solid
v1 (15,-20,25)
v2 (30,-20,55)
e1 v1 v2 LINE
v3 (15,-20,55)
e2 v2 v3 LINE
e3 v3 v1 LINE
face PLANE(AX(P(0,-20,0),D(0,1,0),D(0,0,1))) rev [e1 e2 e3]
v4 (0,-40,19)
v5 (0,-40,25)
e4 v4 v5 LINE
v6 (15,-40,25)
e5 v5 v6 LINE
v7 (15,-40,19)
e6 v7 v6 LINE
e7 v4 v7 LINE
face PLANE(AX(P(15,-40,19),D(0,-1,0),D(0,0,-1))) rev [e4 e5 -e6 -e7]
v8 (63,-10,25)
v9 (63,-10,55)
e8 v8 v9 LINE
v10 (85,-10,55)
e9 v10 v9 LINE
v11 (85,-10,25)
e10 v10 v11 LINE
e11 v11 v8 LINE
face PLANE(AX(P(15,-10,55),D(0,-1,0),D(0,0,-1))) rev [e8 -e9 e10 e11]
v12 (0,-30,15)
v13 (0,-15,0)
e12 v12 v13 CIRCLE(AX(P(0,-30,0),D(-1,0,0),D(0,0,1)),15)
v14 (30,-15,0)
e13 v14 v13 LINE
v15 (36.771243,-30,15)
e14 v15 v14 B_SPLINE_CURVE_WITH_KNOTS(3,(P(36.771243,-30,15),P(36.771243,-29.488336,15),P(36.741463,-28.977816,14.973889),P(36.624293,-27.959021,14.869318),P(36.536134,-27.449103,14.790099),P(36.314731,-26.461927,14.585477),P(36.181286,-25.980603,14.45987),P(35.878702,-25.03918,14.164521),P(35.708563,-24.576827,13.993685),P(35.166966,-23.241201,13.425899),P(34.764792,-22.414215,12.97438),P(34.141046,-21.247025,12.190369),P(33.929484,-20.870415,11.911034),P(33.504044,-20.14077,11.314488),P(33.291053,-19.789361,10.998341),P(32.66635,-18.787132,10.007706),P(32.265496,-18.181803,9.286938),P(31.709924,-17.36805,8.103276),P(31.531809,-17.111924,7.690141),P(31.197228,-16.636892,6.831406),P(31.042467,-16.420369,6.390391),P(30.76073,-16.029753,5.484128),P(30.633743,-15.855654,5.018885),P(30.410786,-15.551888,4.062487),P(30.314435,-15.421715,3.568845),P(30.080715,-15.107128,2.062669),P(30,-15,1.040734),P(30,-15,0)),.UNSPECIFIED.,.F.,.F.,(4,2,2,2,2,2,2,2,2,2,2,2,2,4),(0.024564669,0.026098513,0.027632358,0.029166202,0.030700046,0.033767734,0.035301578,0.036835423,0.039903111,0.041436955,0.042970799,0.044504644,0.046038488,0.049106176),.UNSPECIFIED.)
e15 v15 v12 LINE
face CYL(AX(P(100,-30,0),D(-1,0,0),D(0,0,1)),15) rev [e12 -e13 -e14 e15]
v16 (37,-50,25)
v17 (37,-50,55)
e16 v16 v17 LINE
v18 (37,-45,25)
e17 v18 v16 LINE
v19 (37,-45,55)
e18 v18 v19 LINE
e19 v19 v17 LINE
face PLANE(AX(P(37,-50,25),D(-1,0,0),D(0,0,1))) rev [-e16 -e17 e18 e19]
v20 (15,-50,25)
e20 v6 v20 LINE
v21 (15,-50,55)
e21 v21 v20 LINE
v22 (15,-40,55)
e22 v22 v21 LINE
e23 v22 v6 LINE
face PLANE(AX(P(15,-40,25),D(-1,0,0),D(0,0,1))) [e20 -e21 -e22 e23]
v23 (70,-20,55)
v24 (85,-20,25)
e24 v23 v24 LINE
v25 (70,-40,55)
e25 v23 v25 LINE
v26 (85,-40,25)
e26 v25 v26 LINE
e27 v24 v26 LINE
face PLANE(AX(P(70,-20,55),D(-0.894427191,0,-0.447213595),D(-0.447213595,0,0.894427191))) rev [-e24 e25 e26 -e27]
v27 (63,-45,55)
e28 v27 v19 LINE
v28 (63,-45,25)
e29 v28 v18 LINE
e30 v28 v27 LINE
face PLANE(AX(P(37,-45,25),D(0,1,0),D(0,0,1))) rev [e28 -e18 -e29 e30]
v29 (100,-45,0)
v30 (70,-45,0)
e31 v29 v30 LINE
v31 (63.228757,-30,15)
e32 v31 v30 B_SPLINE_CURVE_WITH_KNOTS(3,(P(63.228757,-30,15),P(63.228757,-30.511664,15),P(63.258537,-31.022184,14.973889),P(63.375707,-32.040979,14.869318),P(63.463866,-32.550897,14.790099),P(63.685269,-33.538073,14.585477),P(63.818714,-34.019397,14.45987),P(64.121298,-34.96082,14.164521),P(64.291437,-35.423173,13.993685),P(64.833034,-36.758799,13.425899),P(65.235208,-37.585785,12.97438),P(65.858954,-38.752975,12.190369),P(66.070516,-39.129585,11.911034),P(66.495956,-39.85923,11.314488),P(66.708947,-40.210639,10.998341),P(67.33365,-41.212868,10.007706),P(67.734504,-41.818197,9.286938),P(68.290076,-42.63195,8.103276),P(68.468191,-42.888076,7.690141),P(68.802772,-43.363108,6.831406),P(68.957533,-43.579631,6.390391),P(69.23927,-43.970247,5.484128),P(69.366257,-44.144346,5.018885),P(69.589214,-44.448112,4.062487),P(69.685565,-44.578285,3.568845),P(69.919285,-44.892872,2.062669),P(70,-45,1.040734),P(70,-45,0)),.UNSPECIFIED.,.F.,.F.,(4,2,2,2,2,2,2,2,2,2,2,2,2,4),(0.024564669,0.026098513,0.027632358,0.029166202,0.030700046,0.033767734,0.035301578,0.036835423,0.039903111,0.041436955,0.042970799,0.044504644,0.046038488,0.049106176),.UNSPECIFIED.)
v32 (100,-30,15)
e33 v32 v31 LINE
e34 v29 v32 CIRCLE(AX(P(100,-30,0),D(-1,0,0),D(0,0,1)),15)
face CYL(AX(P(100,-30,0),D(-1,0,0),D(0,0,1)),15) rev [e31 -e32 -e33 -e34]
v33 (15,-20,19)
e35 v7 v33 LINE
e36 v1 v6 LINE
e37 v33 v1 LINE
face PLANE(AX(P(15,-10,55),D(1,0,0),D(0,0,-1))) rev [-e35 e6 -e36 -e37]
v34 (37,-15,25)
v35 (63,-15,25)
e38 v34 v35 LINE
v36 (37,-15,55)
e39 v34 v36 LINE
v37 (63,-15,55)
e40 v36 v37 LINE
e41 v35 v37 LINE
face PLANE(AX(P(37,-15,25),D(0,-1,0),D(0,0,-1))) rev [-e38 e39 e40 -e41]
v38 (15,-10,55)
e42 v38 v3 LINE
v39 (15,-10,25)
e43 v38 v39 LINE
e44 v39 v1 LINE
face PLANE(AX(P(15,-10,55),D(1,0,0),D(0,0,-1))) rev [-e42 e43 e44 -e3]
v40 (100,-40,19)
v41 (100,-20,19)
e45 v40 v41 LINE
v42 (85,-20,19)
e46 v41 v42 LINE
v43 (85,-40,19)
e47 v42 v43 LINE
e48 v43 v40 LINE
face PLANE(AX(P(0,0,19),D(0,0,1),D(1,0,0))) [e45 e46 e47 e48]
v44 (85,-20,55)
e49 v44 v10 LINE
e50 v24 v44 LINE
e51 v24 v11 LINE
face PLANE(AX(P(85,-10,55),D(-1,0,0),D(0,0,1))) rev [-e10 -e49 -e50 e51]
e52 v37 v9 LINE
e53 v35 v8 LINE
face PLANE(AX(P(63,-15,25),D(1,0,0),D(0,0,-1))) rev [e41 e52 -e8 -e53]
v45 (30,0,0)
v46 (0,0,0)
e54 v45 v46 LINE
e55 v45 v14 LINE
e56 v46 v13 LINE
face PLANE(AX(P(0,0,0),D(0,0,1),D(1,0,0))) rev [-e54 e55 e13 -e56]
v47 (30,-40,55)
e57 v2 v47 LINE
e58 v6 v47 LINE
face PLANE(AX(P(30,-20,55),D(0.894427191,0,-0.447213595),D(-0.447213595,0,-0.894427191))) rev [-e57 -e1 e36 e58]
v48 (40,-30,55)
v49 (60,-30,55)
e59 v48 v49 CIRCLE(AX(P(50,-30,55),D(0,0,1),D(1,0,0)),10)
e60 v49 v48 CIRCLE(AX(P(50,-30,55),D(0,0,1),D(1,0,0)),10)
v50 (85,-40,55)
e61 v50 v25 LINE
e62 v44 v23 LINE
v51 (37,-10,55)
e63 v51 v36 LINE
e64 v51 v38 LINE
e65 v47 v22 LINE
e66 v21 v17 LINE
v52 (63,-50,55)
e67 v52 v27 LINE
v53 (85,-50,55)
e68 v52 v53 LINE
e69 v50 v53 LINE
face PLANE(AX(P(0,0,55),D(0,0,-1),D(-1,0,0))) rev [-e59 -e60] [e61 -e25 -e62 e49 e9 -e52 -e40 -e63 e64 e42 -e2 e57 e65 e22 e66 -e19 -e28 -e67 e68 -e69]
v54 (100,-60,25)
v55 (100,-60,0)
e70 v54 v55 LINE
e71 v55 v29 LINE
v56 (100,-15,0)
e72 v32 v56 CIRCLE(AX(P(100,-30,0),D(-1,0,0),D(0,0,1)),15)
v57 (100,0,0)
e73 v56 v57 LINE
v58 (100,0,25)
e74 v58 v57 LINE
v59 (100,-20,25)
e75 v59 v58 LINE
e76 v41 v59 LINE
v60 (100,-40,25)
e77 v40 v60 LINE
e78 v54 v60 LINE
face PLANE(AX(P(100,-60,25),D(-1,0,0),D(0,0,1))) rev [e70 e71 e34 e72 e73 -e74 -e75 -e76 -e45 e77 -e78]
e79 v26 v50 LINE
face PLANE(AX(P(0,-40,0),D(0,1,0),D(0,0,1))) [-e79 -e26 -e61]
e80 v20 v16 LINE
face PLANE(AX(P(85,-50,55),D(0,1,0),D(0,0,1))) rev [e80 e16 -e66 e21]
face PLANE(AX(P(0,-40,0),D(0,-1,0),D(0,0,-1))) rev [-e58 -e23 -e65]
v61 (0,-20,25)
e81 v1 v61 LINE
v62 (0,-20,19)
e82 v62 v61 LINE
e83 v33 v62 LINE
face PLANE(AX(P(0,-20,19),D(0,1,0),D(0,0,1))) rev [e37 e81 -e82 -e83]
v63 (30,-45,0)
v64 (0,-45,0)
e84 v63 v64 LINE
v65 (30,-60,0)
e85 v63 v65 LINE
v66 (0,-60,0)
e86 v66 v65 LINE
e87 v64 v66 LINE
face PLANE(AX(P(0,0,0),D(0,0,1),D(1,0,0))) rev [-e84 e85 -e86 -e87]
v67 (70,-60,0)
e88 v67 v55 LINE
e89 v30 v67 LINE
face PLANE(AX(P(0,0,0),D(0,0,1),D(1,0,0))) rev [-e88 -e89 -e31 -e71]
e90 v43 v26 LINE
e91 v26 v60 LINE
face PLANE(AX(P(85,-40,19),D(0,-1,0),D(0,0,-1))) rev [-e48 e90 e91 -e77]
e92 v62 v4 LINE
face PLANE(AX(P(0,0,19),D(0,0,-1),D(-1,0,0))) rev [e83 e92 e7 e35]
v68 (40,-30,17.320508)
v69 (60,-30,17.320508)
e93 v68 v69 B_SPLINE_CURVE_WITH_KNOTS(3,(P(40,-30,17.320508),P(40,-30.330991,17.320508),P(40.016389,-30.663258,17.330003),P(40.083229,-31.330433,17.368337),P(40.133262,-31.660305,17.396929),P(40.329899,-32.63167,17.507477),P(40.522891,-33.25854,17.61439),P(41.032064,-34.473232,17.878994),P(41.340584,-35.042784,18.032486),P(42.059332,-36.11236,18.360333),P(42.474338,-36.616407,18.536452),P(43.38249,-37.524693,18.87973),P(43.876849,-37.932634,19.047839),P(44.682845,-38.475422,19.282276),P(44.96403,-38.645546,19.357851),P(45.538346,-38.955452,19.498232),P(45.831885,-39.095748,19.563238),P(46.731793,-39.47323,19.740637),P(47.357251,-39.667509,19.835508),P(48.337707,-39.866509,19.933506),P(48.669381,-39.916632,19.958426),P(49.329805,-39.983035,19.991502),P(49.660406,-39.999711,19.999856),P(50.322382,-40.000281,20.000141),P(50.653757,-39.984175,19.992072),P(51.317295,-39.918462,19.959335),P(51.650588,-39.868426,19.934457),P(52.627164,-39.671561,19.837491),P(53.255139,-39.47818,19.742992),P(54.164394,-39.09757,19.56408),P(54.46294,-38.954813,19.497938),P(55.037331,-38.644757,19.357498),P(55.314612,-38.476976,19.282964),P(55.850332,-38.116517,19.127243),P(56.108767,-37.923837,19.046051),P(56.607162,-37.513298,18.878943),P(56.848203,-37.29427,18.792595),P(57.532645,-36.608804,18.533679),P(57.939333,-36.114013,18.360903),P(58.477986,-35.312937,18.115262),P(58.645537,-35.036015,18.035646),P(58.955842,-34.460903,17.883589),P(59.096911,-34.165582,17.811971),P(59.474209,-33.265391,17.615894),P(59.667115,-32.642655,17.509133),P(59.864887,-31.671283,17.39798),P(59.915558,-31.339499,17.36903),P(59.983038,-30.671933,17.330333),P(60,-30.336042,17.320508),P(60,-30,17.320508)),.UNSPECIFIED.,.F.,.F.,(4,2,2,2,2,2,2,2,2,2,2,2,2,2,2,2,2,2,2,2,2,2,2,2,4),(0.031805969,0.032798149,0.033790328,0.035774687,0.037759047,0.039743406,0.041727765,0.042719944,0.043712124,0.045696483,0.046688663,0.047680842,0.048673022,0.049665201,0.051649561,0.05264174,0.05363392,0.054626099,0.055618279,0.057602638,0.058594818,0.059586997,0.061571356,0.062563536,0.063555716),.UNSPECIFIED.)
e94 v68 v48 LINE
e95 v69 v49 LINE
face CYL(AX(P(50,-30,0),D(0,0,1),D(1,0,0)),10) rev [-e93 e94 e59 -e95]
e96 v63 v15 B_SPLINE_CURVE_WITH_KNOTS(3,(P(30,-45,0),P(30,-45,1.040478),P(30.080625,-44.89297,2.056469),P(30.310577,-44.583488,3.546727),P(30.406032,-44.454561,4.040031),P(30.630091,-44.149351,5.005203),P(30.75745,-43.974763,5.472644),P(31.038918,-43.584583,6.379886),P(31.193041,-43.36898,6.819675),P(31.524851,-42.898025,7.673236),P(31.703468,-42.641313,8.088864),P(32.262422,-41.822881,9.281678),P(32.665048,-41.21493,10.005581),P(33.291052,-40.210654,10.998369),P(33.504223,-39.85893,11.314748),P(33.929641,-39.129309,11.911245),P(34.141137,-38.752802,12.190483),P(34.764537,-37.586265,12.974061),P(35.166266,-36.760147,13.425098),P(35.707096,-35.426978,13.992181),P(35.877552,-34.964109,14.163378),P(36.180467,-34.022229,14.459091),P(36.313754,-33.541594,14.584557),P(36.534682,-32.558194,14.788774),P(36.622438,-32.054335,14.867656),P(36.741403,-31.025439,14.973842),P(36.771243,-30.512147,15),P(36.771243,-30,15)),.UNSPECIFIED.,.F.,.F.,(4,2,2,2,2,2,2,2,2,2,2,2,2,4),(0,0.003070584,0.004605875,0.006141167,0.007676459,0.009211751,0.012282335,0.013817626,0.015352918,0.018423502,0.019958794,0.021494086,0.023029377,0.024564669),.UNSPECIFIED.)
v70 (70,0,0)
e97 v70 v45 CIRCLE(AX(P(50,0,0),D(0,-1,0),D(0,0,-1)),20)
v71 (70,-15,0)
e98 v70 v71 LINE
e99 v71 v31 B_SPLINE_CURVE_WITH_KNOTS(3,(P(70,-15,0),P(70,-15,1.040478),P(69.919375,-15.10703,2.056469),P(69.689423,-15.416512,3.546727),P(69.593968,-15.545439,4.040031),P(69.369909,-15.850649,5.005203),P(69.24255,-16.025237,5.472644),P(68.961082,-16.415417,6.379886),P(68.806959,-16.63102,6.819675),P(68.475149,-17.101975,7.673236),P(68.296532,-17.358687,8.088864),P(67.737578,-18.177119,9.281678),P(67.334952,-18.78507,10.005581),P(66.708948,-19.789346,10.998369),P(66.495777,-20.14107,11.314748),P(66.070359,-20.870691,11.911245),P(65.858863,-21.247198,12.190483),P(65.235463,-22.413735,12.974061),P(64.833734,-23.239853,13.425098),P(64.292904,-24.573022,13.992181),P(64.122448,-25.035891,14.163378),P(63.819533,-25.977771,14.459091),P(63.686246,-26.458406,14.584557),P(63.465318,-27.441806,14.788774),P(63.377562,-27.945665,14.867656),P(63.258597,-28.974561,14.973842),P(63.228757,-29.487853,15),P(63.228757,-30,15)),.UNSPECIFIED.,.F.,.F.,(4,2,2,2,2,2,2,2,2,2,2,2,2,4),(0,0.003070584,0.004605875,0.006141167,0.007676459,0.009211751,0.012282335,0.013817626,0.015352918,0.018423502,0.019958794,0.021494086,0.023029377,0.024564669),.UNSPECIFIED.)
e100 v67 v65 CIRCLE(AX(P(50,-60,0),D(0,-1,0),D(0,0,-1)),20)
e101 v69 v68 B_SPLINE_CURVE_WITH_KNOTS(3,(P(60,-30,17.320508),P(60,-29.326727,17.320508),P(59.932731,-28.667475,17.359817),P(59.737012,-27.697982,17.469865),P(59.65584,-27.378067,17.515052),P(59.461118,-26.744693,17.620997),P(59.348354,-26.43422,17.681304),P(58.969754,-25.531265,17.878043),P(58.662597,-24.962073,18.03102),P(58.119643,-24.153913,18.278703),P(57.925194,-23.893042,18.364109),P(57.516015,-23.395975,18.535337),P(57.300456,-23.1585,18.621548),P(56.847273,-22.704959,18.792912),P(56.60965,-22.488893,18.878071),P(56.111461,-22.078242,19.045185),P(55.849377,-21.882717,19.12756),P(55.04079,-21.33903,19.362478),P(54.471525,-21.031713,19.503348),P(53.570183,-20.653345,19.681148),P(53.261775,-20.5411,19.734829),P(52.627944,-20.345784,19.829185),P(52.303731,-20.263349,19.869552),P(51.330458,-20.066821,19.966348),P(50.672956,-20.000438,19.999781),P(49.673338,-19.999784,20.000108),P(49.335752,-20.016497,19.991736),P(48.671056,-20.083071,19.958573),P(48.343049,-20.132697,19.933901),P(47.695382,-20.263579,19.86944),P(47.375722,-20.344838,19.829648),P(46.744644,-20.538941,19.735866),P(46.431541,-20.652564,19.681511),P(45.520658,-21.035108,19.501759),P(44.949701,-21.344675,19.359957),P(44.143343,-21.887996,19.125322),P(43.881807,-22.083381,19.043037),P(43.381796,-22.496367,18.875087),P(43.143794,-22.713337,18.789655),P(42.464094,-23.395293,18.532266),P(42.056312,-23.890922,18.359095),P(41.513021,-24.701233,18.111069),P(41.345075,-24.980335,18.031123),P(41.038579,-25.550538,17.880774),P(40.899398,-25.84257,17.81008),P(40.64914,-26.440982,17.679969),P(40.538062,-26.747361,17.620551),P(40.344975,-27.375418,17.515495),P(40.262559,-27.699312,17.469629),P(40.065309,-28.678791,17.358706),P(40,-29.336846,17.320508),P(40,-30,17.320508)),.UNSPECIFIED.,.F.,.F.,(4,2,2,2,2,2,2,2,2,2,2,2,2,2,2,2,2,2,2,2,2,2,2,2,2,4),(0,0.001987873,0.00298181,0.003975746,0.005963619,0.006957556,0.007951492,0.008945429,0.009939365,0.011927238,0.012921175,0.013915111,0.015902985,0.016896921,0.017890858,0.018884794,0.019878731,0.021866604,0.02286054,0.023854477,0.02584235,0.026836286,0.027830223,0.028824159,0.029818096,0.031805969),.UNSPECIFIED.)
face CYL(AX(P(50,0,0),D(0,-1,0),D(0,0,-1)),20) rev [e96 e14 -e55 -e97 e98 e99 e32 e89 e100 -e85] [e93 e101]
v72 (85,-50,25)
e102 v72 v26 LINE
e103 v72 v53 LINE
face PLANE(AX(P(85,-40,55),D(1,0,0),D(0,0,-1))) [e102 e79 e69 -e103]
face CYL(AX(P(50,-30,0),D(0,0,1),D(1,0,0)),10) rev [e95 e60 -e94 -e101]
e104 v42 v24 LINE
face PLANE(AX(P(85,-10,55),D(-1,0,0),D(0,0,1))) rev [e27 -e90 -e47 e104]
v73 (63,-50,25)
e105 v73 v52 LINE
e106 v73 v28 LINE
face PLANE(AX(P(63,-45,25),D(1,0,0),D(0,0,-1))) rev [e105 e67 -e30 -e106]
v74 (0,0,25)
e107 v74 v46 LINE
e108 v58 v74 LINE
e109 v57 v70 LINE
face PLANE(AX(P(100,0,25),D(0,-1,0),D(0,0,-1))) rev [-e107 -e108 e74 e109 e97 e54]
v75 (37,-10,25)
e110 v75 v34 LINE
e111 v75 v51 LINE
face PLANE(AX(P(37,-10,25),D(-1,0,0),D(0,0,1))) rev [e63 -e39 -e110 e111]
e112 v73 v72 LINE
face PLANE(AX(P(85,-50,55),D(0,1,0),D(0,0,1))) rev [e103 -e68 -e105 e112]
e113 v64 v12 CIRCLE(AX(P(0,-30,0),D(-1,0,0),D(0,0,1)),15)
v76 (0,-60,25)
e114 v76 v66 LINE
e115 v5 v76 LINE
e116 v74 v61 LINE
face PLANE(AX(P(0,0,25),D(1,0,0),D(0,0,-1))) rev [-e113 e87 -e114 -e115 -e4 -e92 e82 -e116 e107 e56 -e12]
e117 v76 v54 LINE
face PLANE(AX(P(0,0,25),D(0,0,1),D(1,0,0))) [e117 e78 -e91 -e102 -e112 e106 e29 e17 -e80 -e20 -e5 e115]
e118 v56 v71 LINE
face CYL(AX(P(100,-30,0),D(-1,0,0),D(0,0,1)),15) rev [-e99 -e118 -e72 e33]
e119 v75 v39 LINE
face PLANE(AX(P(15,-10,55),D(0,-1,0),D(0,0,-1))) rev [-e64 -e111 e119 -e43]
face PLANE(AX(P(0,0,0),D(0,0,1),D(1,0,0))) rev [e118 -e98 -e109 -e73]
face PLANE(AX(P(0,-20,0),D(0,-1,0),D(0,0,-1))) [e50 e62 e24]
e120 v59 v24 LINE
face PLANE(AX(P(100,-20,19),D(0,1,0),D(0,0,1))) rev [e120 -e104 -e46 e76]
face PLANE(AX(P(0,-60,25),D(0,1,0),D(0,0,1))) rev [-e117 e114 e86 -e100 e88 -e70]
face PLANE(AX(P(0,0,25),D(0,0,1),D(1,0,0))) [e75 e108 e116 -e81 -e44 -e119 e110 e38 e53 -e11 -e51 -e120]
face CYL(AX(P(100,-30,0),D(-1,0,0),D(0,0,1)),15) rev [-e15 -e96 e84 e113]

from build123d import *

# Parameters (mm, degrees)
BASE_PLATE_SKETCH_W        = 100
BASE_PLATE_SKETCH_H        = 60
BASE_PLATE_100X60X25_DEPTH = 25
T_BLOCK_SKETCH_W           = 70
T_BLOCK_SKETCH_H           = 40
T_BLOCK_70X40X30_DEPTH     = 30
SLOT_15X20_SKETCH_W        = 15
SLOT_15X20_SKETCH_H        = 20
SLOT_15X20_DEPTH_6_DEPTH   = 6
SECOND_SLOT_SKETCH_W       = 15
SECOND_SLOT_SKETCH_H       = 20
SECOND_SLOT_DEPTH_6_DEPTH  = 6
SIDE_ARC_NOTCH_DEPTH       = 60
END_ARC_NOTCH_DEPTH        = 100
BLOCK_RECESS_A_SKETCH_W    = 26
BLOCK_RECESS_A_SKETCH_H    = 5
BLOCK_RECESS_A_DEPTH       = 30
BLOCK_RECESS_B_SKETCH_W    = 26
BLOCK_RECESS_B_SKETCH_H    = 5
BLOCK_RECESS_B_DEPTH       = 30
CROSS_HOLE_SKETCH_R        = 10
CROSS_HOLE_DEPTH           = 55
WEDGE_CUT_A_DEPTH          = 30
WEDGE_FILL_A_DEPTH         = 10
WEDGE_CUT_B_DEPTH          = 30
WEDGE_FILL_B_DEPTH         = 10


with BuildPart() as part:
    # Base Plate Sketch → Base Plate 100x60x25 (new body)
    with BuildSketch(Plane.XY):
        with Locations((50, -30)):
            Rectangle(BASE_PLATE_SKETCH_W, BASE_PLATE_SKETCH_H)
    extrude(amount=BASE_PLATE_100X60X25_DEPTH)

    # T-Block Sketch → T-Block 70x40x30 (add)
    with BuildSketch(Plane.XY.offset(25)):
        with Locations((50, -30)):
            Rectangle(T_BLOCK_SKETCH_W, T_BLOCK_SKETCH_H)
    extrude(amount=T_BLOCK_70X40X30_DEPTH)

    # Slot 15x20 Sketch → Slot 15x20 Depth 6 (cut)
    with BuildSketch(Plane.XY.offset(25)):
        with Locations((7.5, -30)):
            Rectangle(SLOT_15X20_SKETCH_W, SLOT_15X20_SKETCH_H)
    extrude(amount=-SLOT_15X20_DEPTH_6_DEPTH, mode=Mode.SUBTRACT)

    # Second Slot Sketch → Second Slot Depth 6 (cut)
    with BuildSketch(Plane.XY.offset(25)):
        with Locations((92.5, -30)):
            Rectangle(SECOND_SLOT_SKETCH_W, SECOND_SLOT_SKETCH_H)
    extrude(amount=-SECOND_SLOT_DEPTH_6_DEPTH, mode=Mode.SUBTRACT)

    # Side Arc Notch Sketch → Side Arc Notch (cut)
    with BuildSketch(Plane.XZ.offset(60)):
        with BuildLine():
            Line((30, 0), (70, 0))
            ThreePointArc((70, 0), (50, 20), (30, 0))
        make_face()
    extrude(amount=-SIDE_ARC_NOTCH_DEPTH, mode=Mode.SUBTRACT)

    # End Arc Notch Sketch → End Arc Notch (cut)
    with BuildSketch(Plane.ZY):
        with BuildLine():
            Line((0, -15), (0, -45))
            ThreePointArc((0, -45), (15, -30), (0, -15))
        make_face()
    extrude(amount=-END_ARC_NOTCH_DEPTH, mode=Mode.SUBTRACT)

    # Block Recess A Sketch → Block Recess A (cut)
    with BuildSketch(Plane.XY.offset(55)):
        with Locations((50, -12.5)):
            Rectangle(BLOCK_RECESS_A_SKETCH_W, BLOCK_RECESS_A_SKETCH_H)
    extrude(amount=-BLOCK_RECESS_A_DEPTH, mode=Mode.SUBTRACT)

    # Block Recess B Sketch → Block Recess B (cut)
    with BuildSketch(Plane.XY.offset(55)):
        with Locations((50, -47.5)):
            Rectangle(BLOCK_RECESS_B_SKETCH_W, BLOCK_RECESS_B_SKETCH_H)
    extrude(amount=-BLOCK_RECESS_B_DEPTH, mode=Mode.SUBTRACT)

    # Cross Hole Sketch → Cross Hole (cut)
    with BuildSketch(Plane.XY.offset(55)):
        with Locations((50, -30)):
            Circle(CROSS_HOLE_SKETCH_R)
    extrude(amount=-CROSS_HOLE_DEPTH, mode=Mode.SUBTRACT)

    # Wedge Cut A Sketch → Wedge Cut A (cut)
    with BuildSketch(Plane.XZ.offset(50)):
        Polygon((15, 55), (30, 55), (15, 25), align=None)
    extrude(amount=-WEDGE_CUT_A_DEPTH, mode=Mode.SUBTRACT)

    # Wedge Fill A Sketch → Wedge Fill A (add)
    with BuildSketch(Plane.XZ.offset(50)):
        Polygon((15, 25), (15, 55), (30, 55), align=None)
    extrude(amount=-WEDGE_FILL_A_DEPTH)

    # Wedge Cut B Sketch → Wedge Cut B (cut)
    with BuildSketch(Plane.XZ.offset(50)):
        Polygon((85, 55), (70, 55), (85, 25), align=None)
    extrude(amount=-WEDGE_CUT_B_DEPTH, mode=Mode.SUBTRACT)

    # Wedge Fill B Sketch → Wedge Fill B (add)
    with BuildSketch(Plane.XZ.offset(50)):
        Polygon((70, 55), (85, 55), (85, 25), align=None)
    extrude(amount=-WEDGE_FILL_B_DEPTH)


solid = part.part
